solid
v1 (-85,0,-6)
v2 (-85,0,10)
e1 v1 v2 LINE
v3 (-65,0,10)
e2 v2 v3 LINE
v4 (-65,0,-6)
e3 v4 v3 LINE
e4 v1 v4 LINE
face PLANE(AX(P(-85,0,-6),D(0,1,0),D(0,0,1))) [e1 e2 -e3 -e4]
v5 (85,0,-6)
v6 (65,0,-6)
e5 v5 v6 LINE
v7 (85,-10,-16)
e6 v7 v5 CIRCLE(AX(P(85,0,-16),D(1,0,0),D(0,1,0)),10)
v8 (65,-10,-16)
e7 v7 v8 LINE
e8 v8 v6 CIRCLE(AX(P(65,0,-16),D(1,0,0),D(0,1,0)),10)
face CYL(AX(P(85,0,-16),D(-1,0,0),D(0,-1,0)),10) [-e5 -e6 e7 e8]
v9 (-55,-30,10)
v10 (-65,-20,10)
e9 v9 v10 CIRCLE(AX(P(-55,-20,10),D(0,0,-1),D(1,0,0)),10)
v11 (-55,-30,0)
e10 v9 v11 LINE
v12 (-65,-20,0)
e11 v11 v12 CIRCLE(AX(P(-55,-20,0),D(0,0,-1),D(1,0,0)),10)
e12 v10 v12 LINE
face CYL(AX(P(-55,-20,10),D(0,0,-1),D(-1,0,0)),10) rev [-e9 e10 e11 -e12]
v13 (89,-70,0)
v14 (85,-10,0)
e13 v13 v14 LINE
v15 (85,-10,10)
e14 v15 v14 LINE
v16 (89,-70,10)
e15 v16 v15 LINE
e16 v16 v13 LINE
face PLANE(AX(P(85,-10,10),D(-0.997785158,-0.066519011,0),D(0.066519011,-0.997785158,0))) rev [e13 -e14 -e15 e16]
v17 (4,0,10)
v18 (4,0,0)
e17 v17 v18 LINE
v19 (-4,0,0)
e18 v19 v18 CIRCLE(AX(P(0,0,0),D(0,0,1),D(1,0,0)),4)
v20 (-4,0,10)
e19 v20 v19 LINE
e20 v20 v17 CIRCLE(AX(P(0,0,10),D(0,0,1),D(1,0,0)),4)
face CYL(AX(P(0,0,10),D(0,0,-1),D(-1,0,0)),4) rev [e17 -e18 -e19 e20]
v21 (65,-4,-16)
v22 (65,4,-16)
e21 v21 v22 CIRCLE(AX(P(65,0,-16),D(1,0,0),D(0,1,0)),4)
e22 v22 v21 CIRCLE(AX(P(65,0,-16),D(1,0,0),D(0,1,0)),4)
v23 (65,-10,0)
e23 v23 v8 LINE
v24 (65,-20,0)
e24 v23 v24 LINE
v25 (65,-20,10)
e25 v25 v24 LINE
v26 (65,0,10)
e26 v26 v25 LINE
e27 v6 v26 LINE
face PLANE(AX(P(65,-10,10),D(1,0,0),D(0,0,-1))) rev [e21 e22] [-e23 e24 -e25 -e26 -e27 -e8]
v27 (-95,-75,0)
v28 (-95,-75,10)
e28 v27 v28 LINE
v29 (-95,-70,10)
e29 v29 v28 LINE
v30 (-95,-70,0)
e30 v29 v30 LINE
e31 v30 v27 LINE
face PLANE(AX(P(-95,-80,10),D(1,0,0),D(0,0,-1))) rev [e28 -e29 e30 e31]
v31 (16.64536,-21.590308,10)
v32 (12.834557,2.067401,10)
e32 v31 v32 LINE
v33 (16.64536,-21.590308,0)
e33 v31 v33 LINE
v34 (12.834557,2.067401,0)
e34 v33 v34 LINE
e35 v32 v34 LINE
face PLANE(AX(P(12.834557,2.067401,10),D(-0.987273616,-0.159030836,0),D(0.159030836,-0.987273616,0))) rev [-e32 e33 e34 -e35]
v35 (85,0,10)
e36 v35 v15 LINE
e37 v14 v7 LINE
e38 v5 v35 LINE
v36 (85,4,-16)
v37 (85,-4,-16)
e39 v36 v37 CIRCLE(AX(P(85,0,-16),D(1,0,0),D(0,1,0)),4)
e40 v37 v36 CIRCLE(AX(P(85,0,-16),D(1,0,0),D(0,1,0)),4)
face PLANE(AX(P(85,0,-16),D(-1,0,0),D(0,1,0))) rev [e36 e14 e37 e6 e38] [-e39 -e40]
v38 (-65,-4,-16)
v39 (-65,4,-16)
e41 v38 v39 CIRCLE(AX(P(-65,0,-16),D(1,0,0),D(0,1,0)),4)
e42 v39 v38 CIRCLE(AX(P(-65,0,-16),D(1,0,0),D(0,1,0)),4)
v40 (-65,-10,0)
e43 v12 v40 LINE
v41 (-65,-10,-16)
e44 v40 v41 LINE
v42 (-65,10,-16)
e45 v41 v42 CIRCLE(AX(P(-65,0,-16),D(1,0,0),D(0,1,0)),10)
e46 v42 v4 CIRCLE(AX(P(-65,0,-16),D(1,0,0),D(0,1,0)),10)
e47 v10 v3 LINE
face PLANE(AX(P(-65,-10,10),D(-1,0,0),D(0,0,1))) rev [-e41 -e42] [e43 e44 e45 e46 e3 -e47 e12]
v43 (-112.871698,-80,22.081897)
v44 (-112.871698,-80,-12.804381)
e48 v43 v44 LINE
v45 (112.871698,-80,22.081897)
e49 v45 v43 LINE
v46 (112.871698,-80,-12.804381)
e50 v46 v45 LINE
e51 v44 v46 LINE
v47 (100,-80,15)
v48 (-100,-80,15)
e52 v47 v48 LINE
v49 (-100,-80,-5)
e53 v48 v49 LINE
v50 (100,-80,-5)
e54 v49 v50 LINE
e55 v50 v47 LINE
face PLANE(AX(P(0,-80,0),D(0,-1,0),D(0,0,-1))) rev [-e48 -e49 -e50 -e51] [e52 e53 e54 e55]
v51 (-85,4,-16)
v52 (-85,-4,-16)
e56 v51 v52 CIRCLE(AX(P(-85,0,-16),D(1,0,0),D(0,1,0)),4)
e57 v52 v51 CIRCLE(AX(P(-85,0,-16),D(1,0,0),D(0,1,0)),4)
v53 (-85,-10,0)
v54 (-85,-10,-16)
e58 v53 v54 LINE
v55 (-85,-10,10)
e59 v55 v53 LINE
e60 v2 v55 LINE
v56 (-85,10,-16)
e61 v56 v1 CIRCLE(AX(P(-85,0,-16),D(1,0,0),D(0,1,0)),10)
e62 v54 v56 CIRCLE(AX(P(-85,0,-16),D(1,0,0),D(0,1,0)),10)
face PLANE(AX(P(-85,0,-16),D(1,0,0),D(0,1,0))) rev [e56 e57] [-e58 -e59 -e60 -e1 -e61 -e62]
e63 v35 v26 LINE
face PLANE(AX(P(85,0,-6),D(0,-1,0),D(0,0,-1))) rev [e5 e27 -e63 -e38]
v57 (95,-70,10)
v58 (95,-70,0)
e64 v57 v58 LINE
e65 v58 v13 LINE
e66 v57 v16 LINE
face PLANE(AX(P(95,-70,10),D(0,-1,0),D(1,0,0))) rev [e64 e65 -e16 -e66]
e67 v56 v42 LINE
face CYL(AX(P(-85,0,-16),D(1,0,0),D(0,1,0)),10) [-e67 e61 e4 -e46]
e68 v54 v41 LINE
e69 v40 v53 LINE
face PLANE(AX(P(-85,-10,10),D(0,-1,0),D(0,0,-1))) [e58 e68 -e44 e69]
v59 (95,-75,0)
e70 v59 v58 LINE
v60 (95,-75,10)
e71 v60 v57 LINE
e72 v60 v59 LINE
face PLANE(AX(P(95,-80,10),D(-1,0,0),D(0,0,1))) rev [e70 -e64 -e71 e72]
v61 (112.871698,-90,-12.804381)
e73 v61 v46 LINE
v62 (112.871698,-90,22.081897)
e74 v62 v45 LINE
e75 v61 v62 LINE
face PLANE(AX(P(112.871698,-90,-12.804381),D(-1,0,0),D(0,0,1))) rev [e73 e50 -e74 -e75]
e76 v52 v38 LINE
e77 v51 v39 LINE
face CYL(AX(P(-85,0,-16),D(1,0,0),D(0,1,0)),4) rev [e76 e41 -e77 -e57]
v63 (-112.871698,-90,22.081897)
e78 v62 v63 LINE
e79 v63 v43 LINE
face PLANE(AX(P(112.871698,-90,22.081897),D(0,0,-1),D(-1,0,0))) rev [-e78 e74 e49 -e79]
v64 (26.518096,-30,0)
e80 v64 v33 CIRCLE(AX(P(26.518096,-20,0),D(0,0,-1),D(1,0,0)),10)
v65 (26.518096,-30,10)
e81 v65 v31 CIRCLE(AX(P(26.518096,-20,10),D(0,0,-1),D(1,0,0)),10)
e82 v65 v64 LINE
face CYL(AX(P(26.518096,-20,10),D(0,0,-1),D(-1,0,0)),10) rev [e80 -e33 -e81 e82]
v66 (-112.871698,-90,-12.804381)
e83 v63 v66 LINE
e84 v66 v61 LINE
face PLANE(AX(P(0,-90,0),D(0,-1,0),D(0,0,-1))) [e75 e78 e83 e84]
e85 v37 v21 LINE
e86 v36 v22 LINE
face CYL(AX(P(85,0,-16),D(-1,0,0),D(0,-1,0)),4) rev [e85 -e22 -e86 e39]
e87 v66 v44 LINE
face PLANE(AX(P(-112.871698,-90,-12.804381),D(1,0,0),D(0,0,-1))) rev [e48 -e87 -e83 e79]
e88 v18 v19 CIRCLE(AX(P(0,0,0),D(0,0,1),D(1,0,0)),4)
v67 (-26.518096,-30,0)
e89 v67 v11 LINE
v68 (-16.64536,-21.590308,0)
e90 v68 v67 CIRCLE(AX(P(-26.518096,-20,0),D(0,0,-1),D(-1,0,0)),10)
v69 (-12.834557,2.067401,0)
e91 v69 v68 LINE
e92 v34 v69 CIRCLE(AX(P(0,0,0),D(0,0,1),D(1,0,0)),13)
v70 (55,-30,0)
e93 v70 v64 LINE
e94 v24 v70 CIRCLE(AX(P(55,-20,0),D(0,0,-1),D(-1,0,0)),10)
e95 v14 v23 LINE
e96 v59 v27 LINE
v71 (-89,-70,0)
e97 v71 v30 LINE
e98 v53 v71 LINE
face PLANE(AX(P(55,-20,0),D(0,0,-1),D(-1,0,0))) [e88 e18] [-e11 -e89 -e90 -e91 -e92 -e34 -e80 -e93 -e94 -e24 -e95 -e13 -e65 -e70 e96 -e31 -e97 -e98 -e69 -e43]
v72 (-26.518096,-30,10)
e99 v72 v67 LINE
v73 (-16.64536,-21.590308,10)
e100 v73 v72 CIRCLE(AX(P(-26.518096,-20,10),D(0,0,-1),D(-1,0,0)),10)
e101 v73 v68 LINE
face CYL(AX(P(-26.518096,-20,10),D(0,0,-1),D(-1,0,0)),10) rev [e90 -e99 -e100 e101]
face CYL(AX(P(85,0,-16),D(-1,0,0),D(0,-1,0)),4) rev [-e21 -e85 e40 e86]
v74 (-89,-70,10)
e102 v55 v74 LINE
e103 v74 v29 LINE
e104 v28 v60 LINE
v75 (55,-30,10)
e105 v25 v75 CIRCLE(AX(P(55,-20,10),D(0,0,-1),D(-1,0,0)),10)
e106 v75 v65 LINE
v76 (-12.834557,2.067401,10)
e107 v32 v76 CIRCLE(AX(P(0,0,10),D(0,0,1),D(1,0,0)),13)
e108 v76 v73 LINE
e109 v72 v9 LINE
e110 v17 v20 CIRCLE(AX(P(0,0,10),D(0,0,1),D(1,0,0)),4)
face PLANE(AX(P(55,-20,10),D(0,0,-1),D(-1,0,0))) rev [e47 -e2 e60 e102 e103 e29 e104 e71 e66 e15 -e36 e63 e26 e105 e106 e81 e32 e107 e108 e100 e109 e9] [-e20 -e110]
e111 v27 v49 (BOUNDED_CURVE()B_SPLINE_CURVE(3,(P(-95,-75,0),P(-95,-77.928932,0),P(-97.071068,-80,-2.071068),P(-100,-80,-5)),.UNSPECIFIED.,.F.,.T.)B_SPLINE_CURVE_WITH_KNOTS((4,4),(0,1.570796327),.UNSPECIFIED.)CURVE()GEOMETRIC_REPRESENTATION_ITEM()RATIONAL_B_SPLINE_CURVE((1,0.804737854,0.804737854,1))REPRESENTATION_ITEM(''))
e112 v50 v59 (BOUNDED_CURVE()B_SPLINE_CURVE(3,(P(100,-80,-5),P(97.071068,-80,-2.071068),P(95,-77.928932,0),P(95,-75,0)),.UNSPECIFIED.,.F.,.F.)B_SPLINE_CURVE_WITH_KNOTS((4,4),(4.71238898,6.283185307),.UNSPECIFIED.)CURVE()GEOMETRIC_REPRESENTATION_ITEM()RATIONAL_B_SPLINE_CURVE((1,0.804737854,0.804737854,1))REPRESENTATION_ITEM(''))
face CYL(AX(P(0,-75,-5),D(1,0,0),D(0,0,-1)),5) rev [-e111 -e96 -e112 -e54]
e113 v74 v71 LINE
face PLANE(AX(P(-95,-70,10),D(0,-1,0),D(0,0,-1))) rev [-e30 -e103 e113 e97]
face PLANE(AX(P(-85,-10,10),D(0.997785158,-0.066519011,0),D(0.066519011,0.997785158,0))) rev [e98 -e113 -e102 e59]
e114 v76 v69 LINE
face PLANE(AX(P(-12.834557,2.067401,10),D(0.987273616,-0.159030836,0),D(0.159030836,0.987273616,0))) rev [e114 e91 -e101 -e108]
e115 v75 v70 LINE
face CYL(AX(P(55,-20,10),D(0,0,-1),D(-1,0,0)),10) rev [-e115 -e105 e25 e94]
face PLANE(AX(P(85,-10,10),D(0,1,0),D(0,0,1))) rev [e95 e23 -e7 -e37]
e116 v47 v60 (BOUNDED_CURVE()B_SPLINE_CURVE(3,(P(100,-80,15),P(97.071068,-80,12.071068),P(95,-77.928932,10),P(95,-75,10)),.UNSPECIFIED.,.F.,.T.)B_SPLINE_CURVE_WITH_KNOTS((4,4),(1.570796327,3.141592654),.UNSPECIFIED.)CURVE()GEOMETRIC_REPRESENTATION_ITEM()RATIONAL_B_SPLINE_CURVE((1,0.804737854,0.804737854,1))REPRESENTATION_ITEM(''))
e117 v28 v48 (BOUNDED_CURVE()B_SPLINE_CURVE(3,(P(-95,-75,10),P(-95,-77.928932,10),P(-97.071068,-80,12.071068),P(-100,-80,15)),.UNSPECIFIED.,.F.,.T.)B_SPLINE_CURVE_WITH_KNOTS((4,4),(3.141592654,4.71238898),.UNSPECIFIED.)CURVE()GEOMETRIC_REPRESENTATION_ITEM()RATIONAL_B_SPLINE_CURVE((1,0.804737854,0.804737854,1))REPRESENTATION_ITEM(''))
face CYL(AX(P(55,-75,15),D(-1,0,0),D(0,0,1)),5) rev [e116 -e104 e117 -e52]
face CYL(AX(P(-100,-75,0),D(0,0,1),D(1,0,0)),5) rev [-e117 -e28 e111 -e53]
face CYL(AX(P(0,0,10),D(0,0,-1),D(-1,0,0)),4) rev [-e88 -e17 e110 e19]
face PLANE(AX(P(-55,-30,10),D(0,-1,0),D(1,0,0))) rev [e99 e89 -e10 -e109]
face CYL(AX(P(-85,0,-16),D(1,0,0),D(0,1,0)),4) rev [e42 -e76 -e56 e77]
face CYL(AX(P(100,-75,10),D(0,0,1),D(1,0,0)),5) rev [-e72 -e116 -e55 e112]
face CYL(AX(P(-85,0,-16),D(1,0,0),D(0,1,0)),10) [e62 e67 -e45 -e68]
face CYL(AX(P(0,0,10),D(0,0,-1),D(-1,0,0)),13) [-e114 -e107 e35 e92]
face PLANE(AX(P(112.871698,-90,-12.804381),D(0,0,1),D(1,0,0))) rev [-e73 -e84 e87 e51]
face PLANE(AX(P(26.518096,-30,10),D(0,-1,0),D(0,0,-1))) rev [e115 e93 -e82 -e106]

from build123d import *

# Parameters (mm, degrees)
SKETCH1_R           = 4
BOSS_EXTRUDE1_DEPTH = 10
SKETCH2_W           = 225.743396996
SKETCH2_H           = 34.886278096
BOSS_EXTRUDE2_DEPTH = 10
SKETCH3_R           = 4
BOSS_EXTRUDE3_DEPTH = 20
FILLET1_R           = 5


with BuildPart() as part:
    # Sketch1 → Boss-Extrude1 (new body)
    with BuildSketch(Plane.XY):
        with BuildLine():
            Line((-85, -10), (-89, -70))
            Line((-89, -70), (-95, -70))
            Line((-95, -70), (-95, -80))
            Line((-95, -80), (95, -80))
            Line((95, -80), (95, -70))
            Line((95, -70), (89, -70))
            Line((89, -70), (85, -10))
            Line((85, -10), (65, -10))
            Line((65, -10), (65, -20))
            ThreePointArc((65, -20), (62.071067812, -27.071067812), (55, -30))
            Line((55, -30), (26.518096199, -30))
            ThreePointArc((26.518096199, -30), (20.033617948, -27.612591006), (16.645360037, -21.590308363))
            Line((16.645360037, -21.590308363), (12.83455701, 2.067400872))
            ThreePointArc((12.83455701, 2.067400872), (0, 13), (-12.83455701, 2.067400872))
            Line((-12.83455701, 2.067400872), (-16.645360037, -21.590308363))
            ThreePointArc((-16.645360037, -21.590308363), (-20.033617948, -27.612591006), (-26.518096199, -30))
            Line((-26.518096199, -30), (-55, -30))
            ThreePointArc((-55, -30), (-62.071067812, -27.071067812), (-65, -20))
            Line((-65, -20), (-65, -10))
            Line((-65, -10), (-85, -10))
        make_face()
        Circle(SKETCH1_R, mode=Mode.SUBTRACT)
    extrude(amount=BOSS_EXTRUDE1_DEPTH)

    # Sketch2 → Boss-Extrude2 (add)
    with BuildSketch(Plane(origin=(0, -80, 0), x_dir=(-1, 0, 0), z_dir=(0, -1, 0))):
        with Locations((0, -4.638757859)):
            Rectangle(SKETCH2_W, SKETCH2_H)
    extrude(amount=BOSS_EXTRUDE2_DEPTH)

    # Sketch3 → Boss-Extrude3 (add)
    with BuildSketch(Plane(origin=(-65, 0, 0), x_dir=(0, 0, -1), z_dir=(1, 0, 0))):
        with BuildLine():
            Line((6, 0), (-10, 0))
            Line((-10, 0), (-10, -10))
            Line((-10, -10), (16, -10))
            ThreePointArc((16, -10), (23.071067812, 7.071067812), (6, 0))
        make_face()
        with Locations(Location((16, 0, 0), (0, 0, 90))):
            Circle(SKETCH3_R, mode=Mode.SUBTRACT)
    boss_extrude3 = extrude(amount=-BOSS_EXTRUDE3_DEPTH)

    # Mirror1: Boss-Extrude3 across plane
    add(boss_extrude3.mirror(Plane(origin=(0, 0, 0), x_dir=(0, 0, 1), z_dir=(1, 0, 0))))

    # Fillet1
    fillet1_edges = [part.edges().sort_by_distance(p)[0] for p in [
        (0, -80, 0),
        (95, -80, 5),
        (-95, -80, 5),
        (0, -80, 10),
    ]]
    fillet(fillet1_edges, radius=FILLET1_R)


solid = part.part
